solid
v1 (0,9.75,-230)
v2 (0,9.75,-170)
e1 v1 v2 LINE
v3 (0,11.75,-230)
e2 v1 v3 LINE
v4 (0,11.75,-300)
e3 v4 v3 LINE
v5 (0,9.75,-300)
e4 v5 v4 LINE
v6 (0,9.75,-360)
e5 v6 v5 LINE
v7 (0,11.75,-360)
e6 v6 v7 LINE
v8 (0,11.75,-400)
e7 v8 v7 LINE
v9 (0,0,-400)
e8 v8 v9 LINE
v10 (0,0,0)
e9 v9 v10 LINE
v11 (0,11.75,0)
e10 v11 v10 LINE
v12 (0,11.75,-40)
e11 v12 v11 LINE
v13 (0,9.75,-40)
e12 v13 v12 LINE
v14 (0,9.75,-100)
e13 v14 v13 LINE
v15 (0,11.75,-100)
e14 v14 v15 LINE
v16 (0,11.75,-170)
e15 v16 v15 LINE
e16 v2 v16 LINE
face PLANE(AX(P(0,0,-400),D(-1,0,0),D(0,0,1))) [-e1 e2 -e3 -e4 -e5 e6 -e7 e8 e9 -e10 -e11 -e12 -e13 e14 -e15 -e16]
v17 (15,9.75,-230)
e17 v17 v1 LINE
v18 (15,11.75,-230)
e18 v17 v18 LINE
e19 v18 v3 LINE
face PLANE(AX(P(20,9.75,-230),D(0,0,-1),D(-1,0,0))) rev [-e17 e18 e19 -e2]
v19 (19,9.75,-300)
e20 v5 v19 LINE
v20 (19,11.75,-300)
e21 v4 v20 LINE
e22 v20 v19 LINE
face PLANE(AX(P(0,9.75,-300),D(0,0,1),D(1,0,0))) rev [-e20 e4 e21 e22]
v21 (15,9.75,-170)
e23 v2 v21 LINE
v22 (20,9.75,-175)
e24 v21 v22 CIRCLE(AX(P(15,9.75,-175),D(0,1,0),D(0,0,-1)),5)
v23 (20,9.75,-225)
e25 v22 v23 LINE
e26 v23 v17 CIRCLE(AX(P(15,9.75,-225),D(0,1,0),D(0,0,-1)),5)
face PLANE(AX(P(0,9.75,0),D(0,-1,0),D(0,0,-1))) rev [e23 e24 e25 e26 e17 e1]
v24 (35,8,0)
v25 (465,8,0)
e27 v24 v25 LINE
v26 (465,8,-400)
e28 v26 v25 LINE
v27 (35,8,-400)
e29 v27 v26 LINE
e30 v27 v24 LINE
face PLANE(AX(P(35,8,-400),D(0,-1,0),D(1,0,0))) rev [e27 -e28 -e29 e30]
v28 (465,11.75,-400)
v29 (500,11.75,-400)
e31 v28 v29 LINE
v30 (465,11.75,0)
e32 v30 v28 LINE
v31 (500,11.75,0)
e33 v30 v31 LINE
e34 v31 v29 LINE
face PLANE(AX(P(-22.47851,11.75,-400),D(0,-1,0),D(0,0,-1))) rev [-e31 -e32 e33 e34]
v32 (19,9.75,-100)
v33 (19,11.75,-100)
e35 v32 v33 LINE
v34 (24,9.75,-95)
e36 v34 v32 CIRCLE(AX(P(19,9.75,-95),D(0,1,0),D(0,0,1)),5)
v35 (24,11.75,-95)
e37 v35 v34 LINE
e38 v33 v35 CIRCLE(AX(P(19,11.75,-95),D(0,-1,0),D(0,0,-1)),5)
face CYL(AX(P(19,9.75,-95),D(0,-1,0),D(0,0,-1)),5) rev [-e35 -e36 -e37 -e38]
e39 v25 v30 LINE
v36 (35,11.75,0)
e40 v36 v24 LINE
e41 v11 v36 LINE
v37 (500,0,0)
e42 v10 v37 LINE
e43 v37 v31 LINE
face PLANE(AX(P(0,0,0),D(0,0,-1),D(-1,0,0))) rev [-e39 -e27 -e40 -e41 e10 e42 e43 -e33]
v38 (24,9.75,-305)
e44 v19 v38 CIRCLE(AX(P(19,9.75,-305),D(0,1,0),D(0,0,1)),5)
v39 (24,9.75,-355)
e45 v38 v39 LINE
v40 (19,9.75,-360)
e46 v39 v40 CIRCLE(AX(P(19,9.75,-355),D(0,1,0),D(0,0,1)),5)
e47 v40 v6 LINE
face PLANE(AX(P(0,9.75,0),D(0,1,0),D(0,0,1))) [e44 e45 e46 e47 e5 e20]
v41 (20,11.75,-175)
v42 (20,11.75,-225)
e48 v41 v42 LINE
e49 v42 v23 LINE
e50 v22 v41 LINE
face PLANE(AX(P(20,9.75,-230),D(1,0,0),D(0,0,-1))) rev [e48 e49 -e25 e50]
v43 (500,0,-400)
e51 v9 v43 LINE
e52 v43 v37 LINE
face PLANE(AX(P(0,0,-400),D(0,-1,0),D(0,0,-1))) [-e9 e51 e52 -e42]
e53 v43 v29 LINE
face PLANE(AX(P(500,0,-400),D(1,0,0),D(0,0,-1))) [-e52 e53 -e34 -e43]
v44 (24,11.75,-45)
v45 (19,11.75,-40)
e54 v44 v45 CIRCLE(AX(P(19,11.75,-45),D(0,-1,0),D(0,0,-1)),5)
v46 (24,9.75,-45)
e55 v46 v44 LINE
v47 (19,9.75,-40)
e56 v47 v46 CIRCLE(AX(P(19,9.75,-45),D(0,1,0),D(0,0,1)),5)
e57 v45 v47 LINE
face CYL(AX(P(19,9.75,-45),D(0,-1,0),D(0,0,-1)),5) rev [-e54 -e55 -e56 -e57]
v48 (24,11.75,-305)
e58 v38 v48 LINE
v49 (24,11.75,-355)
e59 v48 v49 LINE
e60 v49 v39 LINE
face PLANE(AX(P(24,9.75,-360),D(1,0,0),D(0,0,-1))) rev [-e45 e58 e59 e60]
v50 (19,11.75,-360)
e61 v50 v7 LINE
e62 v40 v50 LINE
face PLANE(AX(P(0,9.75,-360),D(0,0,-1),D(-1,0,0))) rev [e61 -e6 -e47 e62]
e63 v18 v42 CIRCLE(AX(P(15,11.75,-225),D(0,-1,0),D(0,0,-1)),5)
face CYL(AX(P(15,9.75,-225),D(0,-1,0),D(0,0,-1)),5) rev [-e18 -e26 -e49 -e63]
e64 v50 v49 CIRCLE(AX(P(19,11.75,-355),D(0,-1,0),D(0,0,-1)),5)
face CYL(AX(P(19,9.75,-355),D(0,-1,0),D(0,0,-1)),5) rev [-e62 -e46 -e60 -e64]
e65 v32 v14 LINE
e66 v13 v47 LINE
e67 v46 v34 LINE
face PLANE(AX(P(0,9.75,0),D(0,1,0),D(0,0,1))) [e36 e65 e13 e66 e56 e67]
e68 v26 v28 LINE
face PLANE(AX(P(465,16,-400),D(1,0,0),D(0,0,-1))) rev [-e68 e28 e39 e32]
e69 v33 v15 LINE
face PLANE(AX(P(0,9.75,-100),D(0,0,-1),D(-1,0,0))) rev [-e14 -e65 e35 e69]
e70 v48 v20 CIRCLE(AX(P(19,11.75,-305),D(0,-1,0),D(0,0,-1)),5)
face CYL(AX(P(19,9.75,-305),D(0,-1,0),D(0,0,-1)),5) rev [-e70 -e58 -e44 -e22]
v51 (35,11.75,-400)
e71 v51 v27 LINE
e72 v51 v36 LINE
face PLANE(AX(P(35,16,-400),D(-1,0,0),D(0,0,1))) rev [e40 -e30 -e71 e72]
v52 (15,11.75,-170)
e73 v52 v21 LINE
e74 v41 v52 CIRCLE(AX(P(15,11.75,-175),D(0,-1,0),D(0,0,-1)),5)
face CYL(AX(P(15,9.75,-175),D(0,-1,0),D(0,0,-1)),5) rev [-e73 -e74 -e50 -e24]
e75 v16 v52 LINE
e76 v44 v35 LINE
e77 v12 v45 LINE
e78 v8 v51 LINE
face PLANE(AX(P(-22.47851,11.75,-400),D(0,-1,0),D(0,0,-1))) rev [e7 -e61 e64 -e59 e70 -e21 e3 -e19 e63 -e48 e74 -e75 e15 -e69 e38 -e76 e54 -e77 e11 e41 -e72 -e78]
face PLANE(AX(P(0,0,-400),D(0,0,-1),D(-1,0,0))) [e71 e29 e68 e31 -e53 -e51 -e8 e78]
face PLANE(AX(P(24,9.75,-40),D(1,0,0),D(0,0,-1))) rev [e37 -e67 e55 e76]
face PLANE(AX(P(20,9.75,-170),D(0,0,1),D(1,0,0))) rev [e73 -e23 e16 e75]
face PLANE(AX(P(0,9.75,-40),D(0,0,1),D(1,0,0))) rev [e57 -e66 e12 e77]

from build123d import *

# Parameters (mm, degrees)
SKETCH1_W           = 500
SKETCH1_H           = 24
BOSS_EXTRUDE1_DEPTH = 400
SKETCH2_W           = 430
SKETCH2_H           = 8
CUT_EXTRUDE1_DEPTH  = 641.762046317
SKETCH3_W           = 544.957019416
SKETCH3_H           = 0.5
CUT_EXTRUDE2_DEPTH  = 641.762046317
SKETCH12_W          = 569.007892772
SKETCH12_H          = 39.328779912
CUT_EXTRUDE3_DEPTH  = 641.762046317
SKETCH16_W          = 24
SKETCH16_H          = 60
SKETCH16_W_2        = 20
CUT_EXTRUDE4_DEPTH  = 2
FILLET1_R           = 5


with BuildPart() as part:
    # Sketch1 → Boss-Extrude1 (new body)
    with BuildSketch(Plane.XY):
        with Locations((250, 12)):
            Rectangle(SKETCH1_W, SKETCH1_H)
    extrude(amount=-BOSS_EXTRUDE1_DEPTH)

    # Sketch2 → Cut-Extrude1 (cut, through all)
    with BuildSketch(Plane.XY):
        with Locations((250, 12)):
            Rectangle(SKETCH2_W, SKETCH2_H)
    extrude(amount=-CUT_EXTRUDE1_DEPTH, mode=Mode.SUBTRACT)

    # Sketch3 → Cut-Extrude2 (cut, through all)
    with BuildSketch(Plane.XY):
        with Locations((250, 12)):
            Rectangle(SKETCH3_W, SKETCH3_H)
    extrude(amount=-CUT_EXTRUDE2_DEPTH, mode=Mode.SUBTRACT)


with BuildPart() as cut_extrude2_piece_1:
    # of the separate pieces the step leaves, piece 1, a body of its own (cut_extrude2_pieces)
    add(part.part.solids().sort_by_distance((0, 0, 0))[0])

    # Sketch16 → Cut-Extrude4 (cut)
    with BuildSketch(Plane(origin=(0, 11.75, 0), x_dir=(1, 0, 0), z_dir=(0, 1, 0))):
        with Locations((12, 330)):
            Rectangle(SKETCH16_W, SKETCH16_H)
        with Locations((12, 70)):
            Rectangle(SKETCH16_W, SKETCH16_H)
        with Locations((10, 200)):
            Rectangle(SKETCH16_W_2, SKETCH16_H)
    extrude(amount=-CUT_EXTRUDE4_DEPTH, mode=Mode.SUBTRACT)

    # Fillet1
    fillet1_edges = [cut_extrude2_piece_1.edges().sort_by_distance(p)[0] for p in [
        (24, 10.75, -360),
        (24, 10.75, -300),
        (24, 10.75, -40),
        (24, 10.75, -100),
        (20, 10.75, -230),
        (20, 10.75, -170),
    ]]
    fillet(fillet1_edges, radius=FILLET1_R)


with BuildPart() as cut_extrude2_piece_2:
    # of the separate pieces the step leaves, piece 2, a body of its own (cut_extrude2_pieces)
    add(part.part.solids().sort_by_distance((0, 24, 0))[0])

    # Sketch12 → Cut-Extrude3 (cut, through all)
    with BuildSketch(Plane.XY):
        with Locations((265.175540793, 31.664389956)):
            Rectangle(SKETCH12_W, SKETCH12_H)
    extrude(amount=-CUT_EXTRUDE3_DEPTH, mode=Mode.SUBTRACT)


solid = cut_extrude2_piece_1.part
